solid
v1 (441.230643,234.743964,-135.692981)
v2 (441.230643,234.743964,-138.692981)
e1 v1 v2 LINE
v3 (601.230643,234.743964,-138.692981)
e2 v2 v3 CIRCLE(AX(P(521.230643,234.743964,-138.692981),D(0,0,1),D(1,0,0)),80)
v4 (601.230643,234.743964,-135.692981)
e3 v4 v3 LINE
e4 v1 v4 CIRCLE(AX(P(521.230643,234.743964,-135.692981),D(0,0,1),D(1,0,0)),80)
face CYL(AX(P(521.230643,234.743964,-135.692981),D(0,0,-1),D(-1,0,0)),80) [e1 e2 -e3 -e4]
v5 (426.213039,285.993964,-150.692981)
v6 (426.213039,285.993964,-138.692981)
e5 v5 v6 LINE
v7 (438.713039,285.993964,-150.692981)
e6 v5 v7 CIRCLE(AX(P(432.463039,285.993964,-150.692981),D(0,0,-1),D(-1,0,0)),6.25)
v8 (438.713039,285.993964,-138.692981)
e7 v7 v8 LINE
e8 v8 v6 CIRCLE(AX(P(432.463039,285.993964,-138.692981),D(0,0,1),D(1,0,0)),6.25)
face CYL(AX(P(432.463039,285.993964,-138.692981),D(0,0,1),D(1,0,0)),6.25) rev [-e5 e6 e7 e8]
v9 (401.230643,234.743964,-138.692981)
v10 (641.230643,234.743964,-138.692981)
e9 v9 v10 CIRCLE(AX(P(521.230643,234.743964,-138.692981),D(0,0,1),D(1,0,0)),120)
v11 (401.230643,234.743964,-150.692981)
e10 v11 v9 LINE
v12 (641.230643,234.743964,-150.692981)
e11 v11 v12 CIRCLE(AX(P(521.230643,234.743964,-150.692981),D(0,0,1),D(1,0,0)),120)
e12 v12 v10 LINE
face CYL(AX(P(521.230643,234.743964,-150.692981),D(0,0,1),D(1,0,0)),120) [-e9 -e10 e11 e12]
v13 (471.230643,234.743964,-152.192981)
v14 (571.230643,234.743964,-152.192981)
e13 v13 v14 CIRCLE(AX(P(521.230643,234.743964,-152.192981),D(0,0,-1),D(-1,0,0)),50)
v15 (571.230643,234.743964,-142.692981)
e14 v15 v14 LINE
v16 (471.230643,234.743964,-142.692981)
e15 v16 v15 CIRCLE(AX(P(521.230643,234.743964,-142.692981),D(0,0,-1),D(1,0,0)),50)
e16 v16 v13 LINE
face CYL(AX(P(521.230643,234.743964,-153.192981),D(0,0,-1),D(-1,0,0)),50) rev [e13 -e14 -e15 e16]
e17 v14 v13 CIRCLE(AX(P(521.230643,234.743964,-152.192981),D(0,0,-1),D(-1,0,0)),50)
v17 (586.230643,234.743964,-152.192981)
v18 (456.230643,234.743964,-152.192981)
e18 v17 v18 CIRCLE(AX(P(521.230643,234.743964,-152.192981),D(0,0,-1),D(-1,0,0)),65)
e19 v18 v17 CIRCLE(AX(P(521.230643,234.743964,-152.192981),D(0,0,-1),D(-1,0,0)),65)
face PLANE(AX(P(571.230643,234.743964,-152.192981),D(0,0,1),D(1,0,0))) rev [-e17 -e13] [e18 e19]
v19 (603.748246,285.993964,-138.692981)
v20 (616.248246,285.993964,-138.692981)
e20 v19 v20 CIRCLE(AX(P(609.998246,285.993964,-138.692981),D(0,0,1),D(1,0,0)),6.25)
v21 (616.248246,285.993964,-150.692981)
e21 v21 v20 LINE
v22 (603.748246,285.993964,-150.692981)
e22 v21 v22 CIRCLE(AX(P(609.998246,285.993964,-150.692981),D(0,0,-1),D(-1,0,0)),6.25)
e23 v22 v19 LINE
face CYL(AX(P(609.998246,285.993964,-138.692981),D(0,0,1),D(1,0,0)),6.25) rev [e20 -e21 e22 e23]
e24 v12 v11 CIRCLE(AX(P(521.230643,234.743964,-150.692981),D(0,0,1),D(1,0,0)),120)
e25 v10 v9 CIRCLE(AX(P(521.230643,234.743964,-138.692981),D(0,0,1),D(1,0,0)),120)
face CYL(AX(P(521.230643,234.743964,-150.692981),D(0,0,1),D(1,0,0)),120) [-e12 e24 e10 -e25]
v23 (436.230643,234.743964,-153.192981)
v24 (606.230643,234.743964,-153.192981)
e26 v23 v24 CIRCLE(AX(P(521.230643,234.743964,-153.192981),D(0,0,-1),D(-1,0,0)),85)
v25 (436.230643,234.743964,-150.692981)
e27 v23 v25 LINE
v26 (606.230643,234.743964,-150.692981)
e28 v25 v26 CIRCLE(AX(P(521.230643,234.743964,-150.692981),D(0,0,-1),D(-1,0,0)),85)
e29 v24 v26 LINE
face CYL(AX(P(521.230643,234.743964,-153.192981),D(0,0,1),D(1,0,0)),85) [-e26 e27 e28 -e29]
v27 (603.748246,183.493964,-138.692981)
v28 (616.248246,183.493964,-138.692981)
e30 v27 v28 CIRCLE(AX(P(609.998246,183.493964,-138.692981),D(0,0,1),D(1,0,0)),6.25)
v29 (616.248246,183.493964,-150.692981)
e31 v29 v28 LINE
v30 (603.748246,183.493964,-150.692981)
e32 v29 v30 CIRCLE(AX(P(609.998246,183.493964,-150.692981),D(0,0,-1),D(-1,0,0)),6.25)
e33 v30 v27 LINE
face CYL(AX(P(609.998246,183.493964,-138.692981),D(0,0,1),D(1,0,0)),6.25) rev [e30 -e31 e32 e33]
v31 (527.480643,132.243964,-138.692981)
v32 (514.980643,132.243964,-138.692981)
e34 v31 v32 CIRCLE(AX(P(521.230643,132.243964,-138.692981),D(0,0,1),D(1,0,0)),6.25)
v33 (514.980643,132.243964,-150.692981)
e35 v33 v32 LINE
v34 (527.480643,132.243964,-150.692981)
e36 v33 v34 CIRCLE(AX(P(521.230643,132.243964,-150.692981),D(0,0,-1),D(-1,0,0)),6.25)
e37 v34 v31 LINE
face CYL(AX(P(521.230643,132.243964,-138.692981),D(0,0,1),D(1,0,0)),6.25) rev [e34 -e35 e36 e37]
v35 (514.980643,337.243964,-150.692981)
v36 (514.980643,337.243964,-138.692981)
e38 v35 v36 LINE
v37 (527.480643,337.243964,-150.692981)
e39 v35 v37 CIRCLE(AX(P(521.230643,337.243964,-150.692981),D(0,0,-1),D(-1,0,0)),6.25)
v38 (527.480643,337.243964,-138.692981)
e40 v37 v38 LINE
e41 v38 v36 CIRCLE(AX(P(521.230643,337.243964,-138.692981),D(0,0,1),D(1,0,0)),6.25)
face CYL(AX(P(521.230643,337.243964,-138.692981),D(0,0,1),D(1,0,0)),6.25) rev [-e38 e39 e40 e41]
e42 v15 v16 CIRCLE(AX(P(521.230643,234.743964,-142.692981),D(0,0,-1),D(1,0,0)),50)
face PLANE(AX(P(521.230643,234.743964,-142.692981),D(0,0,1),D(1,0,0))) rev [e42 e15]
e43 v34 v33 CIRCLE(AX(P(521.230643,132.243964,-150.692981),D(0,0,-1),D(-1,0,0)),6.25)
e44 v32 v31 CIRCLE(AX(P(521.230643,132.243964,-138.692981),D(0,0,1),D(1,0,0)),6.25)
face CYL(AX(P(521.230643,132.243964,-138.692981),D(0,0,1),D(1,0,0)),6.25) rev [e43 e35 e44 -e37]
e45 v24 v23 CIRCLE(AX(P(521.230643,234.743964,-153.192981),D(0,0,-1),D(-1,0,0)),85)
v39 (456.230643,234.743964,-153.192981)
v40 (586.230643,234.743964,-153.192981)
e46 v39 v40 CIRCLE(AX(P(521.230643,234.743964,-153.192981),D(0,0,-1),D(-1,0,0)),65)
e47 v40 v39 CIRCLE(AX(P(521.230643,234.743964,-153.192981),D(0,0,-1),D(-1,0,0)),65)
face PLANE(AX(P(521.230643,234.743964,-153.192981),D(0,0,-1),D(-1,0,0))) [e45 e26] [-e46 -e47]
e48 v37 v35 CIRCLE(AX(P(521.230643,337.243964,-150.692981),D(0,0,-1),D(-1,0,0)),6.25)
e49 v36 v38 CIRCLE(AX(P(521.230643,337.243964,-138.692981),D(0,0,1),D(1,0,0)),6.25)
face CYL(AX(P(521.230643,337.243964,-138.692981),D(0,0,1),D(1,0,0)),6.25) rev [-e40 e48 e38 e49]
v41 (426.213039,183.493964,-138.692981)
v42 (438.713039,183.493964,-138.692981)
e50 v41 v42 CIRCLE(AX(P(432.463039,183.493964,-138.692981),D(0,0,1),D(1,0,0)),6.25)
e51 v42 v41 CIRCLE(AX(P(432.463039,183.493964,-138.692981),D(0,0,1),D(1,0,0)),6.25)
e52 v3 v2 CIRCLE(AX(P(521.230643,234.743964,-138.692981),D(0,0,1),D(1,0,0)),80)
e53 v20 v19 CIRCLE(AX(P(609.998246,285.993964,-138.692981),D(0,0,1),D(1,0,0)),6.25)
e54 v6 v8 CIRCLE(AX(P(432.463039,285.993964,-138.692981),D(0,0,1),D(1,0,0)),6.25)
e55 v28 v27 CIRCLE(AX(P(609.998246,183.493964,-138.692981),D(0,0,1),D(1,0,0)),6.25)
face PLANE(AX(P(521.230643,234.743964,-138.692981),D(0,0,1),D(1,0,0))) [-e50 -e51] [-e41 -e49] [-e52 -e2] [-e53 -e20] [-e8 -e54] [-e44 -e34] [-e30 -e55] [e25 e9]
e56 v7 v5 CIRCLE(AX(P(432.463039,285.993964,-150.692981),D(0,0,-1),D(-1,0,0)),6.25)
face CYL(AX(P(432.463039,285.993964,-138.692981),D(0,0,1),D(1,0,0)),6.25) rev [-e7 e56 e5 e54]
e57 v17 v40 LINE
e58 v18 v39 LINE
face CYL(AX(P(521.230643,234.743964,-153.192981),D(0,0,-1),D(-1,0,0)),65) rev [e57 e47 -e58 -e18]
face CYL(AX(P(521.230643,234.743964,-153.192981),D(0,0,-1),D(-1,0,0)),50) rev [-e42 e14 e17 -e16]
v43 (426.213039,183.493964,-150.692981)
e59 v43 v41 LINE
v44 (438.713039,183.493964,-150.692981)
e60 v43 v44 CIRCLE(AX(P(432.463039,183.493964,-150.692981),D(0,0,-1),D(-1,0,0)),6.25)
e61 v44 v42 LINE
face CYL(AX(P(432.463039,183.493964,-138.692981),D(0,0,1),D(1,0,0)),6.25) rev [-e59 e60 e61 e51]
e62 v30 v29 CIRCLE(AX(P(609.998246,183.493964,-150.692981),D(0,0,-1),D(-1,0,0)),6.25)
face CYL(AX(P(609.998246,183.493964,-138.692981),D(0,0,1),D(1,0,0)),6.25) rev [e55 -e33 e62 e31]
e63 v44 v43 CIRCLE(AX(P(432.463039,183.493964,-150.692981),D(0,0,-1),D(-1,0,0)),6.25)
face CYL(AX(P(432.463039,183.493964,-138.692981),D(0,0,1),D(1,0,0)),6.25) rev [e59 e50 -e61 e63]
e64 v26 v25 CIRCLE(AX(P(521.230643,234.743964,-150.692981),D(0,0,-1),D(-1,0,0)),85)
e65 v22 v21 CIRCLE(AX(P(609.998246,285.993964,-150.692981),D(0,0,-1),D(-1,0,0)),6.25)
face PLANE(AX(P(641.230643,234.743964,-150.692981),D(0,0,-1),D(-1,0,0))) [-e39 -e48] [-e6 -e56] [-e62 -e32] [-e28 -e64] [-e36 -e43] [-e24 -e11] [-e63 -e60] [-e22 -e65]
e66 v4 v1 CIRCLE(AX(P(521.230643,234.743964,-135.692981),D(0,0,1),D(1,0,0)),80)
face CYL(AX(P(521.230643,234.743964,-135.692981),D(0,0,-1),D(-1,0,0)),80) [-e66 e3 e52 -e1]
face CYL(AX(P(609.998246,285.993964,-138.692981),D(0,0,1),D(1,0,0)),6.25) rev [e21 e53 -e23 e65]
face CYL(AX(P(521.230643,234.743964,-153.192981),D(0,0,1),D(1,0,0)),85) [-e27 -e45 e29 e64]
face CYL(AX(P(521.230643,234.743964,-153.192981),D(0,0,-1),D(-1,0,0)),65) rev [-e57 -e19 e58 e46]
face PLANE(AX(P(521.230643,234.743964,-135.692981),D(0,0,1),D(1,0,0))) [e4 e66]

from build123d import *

# Parameters (mm, degrees)
SKETCH1_W                         = 120
SKETCH1_H                         = 12
SKETCH2_R                         = 85
BOSS_EXTRUDE1_DEPTH               = 2.5
SKETCH3_R                         = 80
BOSS_EXTRUDE2_DEPTH               = 3
F_12_5_12_5_DIAMETER_HOLE1_D      = 12.5
F_12_5_12_5_DIAMETER_HOLE1_DEPTH  = 14.5
M90_COUNTERBORE_HOLE1_D           = 100
M90_COUNTERBORE_HOLE1_CBORE_D     = 130
M90_COUNTERBORE_HOLE1_CBORE_DEPTH = 1
SKETCH8_R                         = 50.101943112
BOSS_EXTRUDE3_DEPTH               = 7


with BuildPart() as part:
    # Sketch1 → Revolve1 (revolve)
    with BuildSketch(Plane(origin=(0, 234.743963655, 0), x_dir=(1, 0, 0), z_dir=(0, 1, 0))):
        with Locations((581.230642584, 144.692981355)):
            Rectangle(SKETCH1_W, SKETCH1_H)
    revolve(axis=Axis((521.230642584, 234.743963655, -150.692981355), (0, 0, 1)))

    # Sketch2 → Boss-Extrude1 (add)
    with BuildSketch(Plane(origin=(0, 0, -150.692981355), x_dir=(-1, 0, 0), z_dir=(0, 0, -1))):
        with Locations((-521.230642584, 234.743963655)):
            Circle(SKETCH2_R)
    extrude(amount=BOSS_EXTRUDE1_DEPTH)

    # Sketch3 → Boss-Extrude2 (add)
    with BuildSketch(Plane.XY.offset(-138.692981355)):
        with Locations((521.230642584, 234.743963655)):
            Circle(SKETCH3_R)
    extrude(amount=BOSS_EXTRUDE2_DEPTH)

    # Ø12.5 (12.5) Diameter Hole1
    with Locations(Plane.XY.offset(-138.692981355)):
        with Locations((521.230642584, 337.243963655), (609.998246472, 285.993963655), (432.463038696, 285.993963655), (432.463038696, 183.493963655), (521.230642584, 132.243963655), (609.998246472, 183.493963655)):
            Hole(F_12_5_12_5_DIAMETER_HOLE1_D / 2, depth=F_12_5_12_5_DIAMETER_HOLE1_DEPTH)

    # M90 counterbore hole1 (through all)
    with Locations(Plane(origin=(0, 0, -153.192981355), x_dir=(-1, 0, 0), z_dir=(0, 0, -1))):
        with Locations((-521.230642584, 234.743963655)):
            CounterBoreHole(M90_COUNTERBORE_HOLE1_D / 2, M90_COUNTERBORE_HOLE1_CBORE_D / 2, M90_COUNTERBORE_HOLE1_CBORE_DEPTH)

    # Sketch8 → Boss-Extrude3 (add)
    with BuildSketch(Plane.XY.offset(-135.692981355)):
        with Locations((521.230642584, 234.743963655)):
            Circle(SKETCH8_R)
    extrude(amount=-BOSS_EXTRUDE3_DEPTH)


solid = part.part
